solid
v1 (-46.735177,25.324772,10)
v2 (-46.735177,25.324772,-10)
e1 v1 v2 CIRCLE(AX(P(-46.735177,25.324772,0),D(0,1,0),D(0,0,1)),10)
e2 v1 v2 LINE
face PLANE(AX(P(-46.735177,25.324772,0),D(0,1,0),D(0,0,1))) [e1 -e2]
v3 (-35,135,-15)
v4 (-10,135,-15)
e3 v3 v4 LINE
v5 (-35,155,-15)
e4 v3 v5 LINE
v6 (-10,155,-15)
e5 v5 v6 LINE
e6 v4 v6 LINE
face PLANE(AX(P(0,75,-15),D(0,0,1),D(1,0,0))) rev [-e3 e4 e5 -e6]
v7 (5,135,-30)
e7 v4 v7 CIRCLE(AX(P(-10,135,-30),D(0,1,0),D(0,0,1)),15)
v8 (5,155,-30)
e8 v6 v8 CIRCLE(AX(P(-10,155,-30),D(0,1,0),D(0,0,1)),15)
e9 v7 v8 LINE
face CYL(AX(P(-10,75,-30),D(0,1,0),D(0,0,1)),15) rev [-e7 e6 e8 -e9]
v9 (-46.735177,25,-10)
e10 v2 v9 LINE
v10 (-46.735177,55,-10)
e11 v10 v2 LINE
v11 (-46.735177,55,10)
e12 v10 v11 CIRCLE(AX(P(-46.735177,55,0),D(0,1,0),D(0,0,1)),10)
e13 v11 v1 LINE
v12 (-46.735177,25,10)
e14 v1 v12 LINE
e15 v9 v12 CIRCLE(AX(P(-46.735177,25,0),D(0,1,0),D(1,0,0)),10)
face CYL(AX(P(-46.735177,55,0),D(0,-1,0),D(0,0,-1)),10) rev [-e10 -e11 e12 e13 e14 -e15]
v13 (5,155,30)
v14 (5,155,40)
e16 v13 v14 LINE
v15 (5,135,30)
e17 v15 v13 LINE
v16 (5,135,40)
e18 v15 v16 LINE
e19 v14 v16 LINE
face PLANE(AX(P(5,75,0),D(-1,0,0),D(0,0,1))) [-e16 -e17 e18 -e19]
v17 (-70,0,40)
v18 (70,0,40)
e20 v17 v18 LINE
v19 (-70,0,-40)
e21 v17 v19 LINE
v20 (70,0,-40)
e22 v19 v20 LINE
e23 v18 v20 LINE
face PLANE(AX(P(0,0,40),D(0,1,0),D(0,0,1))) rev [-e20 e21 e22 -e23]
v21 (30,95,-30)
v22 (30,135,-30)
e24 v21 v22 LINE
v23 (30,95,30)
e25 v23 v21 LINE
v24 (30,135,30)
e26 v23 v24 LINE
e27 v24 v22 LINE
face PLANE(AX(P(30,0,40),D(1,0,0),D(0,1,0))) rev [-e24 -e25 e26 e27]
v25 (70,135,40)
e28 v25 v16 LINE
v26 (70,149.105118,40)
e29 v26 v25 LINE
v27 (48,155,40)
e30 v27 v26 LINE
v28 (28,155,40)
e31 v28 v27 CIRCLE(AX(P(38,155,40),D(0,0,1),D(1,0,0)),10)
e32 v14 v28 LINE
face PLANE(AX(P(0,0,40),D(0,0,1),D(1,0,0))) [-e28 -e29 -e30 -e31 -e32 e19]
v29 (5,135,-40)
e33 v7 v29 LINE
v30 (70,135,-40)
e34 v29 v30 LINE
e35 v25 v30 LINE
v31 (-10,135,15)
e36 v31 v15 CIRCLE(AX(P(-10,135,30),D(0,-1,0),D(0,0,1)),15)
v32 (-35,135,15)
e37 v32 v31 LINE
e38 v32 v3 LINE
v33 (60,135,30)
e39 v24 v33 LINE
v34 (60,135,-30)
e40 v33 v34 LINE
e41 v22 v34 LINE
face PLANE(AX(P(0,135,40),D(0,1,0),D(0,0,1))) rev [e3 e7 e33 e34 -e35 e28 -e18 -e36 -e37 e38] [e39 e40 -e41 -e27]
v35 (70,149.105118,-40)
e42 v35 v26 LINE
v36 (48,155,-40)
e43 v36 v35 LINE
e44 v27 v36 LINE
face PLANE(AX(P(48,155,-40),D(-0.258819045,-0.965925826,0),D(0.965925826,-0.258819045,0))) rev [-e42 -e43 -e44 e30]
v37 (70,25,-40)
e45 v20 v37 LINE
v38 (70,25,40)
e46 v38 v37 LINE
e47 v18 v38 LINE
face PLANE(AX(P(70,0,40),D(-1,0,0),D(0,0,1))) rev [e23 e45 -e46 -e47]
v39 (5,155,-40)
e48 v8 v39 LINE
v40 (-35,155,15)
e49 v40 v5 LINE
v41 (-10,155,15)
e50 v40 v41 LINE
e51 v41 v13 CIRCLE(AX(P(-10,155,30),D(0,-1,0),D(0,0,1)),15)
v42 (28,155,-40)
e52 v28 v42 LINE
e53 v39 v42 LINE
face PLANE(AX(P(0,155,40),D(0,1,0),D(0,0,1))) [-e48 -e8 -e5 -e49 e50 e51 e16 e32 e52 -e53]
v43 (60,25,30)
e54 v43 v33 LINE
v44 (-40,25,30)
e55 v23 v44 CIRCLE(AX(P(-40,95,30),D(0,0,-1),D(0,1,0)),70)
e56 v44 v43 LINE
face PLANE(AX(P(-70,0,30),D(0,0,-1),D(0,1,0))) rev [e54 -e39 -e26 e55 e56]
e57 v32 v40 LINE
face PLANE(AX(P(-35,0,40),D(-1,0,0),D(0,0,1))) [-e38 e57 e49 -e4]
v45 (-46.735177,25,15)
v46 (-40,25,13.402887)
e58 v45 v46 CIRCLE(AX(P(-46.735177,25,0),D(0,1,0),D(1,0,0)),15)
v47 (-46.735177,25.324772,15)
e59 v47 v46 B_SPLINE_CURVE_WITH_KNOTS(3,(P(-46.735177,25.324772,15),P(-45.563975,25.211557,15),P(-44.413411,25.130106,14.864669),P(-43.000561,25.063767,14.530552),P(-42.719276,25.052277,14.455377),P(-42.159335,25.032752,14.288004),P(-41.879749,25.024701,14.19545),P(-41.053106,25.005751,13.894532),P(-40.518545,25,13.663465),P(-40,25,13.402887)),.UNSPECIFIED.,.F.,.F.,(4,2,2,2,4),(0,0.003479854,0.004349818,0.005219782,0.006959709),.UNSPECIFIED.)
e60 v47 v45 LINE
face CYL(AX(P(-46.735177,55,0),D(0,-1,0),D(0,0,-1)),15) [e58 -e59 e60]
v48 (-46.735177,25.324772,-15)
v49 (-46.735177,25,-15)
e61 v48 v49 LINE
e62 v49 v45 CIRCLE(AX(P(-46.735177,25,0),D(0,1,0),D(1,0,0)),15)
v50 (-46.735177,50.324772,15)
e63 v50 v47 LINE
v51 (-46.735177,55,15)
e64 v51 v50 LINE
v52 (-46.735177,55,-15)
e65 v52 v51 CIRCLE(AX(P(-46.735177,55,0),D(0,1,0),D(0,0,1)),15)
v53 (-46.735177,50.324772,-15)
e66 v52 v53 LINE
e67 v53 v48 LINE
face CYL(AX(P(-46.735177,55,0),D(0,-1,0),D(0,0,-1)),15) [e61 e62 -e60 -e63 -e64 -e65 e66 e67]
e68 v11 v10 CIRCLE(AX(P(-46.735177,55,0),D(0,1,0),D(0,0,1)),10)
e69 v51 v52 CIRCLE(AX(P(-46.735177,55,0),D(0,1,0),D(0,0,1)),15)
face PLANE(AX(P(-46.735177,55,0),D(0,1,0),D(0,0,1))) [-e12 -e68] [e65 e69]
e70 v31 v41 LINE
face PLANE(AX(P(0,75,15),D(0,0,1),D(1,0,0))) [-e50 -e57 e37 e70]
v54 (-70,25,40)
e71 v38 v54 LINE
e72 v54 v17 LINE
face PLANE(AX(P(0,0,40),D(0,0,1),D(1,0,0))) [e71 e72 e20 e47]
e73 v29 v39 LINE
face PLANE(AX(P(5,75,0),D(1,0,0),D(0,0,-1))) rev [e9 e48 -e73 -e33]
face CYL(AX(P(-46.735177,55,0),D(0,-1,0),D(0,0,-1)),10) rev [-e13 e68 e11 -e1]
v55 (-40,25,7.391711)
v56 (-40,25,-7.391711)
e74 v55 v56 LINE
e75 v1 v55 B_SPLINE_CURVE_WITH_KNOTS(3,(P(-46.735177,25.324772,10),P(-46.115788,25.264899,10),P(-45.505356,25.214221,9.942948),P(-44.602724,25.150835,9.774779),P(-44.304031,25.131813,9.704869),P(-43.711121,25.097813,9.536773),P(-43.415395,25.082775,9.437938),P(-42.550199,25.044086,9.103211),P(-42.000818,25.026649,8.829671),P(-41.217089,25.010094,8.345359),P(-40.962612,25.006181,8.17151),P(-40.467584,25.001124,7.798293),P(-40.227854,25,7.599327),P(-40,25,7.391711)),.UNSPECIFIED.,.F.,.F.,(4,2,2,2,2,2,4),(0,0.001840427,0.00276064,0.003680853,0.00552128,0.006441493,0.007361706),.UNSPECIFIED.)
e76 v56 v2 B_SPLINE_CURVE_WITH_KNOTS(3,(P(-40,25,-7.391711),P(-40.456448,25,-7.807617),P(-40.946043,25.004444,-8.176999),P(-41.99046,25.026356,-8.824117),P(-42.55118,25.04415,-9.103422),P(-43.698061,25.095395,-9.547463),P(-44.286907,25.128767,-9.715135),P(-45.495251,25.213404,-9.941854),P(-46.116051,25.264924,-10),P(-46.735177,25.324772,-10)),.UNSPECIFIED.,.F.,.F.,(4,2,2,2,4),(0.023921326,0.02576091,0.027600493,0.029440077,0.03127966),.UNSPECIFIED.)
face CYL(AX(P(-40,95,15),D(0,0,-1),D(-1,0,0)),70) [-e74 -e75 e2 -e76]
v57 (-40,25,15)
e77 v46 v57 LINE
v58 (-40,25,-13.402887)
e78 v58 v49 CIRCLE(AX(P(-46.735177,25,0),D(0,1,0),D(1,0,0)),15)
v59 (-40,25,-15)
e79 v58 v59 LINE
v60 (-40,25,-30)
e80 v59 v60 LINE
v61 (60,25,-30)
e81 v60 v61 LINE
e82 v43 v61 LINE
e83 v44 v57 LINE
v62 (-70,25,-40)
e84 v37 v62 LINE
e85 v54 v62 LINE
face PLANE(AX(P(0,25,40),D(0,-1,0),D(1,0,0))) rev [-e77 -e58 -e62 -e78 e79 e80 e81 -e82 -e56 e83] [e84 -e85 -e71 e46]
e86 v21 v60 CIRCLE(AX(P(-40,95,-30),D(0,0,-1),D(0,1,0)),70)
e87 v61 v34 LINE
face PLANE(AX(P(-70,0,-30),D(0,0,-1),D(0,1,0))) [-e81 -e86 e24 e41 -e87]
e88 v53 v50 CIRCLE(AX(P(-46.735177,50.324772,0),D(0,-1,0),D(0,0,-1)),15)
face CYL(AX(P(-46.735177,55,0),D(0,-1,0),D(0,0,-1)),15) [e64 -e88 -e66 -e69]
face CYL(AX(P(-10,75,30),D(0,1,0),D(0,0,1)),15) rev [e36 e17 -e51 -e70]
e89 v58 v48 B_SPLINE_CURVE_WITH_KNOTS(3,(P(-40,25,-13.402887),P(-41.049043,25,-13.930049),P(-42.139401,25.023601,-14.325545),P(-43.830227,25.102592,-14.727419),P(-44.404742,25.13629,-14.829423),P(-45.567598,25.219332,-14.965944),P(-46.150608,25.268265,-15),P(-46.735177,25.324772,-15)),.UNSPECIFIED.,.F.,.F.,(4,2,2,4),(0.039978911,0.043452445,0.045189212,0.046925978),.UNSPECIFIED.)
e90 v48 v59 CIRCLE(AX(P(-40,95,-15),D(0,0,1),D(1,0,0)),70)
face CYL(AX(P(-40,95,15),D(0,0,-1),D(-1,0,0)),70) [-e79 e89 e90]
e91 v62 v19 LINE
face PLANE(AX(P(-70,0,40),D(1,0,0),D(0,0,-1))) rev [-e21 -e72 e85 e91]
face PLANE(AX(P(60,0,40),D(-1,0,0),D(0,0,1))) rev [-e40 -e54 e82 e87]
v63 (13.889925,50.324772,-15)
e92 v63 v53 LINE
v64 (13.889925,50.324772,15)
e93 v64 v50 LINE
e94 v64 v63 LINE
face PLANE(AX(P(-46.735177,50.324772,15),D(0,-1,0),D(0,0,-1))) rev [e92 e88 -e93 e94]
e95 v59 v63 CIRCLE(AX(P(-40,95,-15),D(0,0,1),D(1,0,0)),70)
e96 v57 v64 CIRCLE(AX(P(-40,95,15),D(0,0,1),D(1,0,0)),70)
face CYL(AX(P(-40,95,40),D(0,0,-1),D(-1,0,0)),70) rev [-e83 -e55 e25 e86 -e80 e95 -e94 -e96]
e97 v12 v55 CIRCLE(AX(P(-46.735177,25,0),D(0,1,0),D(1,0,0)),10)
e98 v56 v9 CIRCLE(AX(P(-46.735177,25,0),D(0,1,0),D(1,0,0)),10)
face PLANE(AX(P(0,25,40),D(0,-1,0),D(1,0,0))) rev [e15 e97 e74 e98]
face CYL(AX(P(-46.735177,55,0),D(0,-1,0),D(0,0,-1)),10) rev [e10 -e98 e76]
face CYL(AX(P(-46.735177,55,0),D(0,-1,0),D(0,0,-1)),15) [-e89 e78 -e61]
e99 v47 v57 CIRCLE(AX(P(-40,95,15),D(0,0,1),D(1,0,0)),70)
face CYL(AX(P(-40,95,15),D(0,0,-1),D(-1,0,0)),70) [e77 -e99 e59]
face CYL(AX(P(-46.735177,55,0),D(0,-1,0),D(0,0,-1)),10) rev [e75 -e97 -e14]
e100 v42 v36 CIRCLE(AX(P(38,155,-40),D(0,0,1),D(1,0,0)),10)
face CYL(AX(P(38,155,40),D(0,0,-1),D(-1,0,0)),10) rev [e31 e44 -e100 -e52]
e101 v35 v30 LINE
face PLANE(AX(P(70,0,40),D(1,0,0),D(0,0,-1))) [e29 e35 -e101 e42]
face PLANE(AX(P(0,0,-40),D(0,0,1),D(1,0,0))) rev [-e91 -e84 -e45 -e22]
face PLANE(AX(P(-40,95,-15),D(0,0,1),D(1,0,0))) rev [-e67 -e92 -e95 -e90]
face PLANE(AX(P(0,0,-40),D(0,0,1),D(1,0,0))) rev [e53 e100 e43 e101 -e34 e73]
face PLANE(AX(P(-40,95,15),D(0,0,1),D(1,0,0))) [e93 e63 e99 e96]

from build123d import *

# Parameters (mm, degrees)
BRACKET_BODY_DEPTH          = 40
BASE_RECESS_SKETCH_W        = 10
BASE_RECESS_SKETCH_H        = 110
BASE_RECESS_CUT_DEPTH       = 207.215906273
CRADLE_GROOVE_R15_DEPTH     = 80
TOP_CHAMFER_CUT_15DEG_DEPTH = 80
PIN_BOSS_SKETCH_R           = 15
PIN_BOSS_SKETCH_R_2         = 10
PIN_BOSS_DEPTH              = 55
CURVED_WEB_DEPTH            = 15
PIN_START                   = -25
PIN_BORE_SKETCH_R           = 10
PIN_BORE_20_DEPTH           = 25


with BuildPart() as part:
    # Bracket Profile Sketch → Bracket Body (new, symmetric)
    with BuildSketch(Plane.XY):
        with BuildLine():
            Line((-40, 25), (60, 25))
            Line((60, 25), (60, 135))
            Line((60, 135), (70, 135))
            Line((70, 135), (70, 155))
            Line((70, 155), (48, 155))
            ThreePointArc((48, 155), (38, 145), (28, 155))
            Line((28, 155), (-35, 155))
            Line((-35, 155), (-35, 135))
            Line((-35, 135), (30, 135))
            Line((30, 135), (30, 95))
            ThreePointArc((30, 95), (9.497474683, 45.502525317), (-40, 25))
        make_face()
        Polygon((-70, 25), (-70, 0), (0, 0), (70, 0), (70, 25), align=None)
    extrude(amount=BRACKET_BODY_DEPTH, both=True)

    # Base Recess Sketch → Base Recess Cut (cut, through all)
    with BuildSketch(Plane(origin=(60, 0, 0), x_dir=(0, 0, -1), z_dir=(1, 0, 0))):
        with Locations((35, 80)):
            Rectangle(BASE_RECESS_SKETCH_W, BASE_RECESS_SKETCH_H)
        with Locations((-35, 80)):
            Rectangle(BASE_RECESS_SKETCH_W, BASE_RECESS_SKETCH_H)
    extrude(amount=-BASE_RECESS_CUT_DEPTH, mode=Mode.SUBTRACT)

    # Cradle Groove Sketch → Cradle Groove R15 (cut)
    with BuildSketch(Plane(origin=(0, 155, 0), x_dir=(1, 0, 0), z_dir=(0, 1, 0))):
        with BuildLine():
            Line((-35, 40), (-35, 15))
            Line((-35, 15), (-10, 15))
            ThreePointArc((-10, 15), (0.606601718, 19.393398282), (5, 30))
            Line((5, 30), (5, 40))
            Line((5, 40), (-35, 40))
        make_face()
        with BuildLine():
            Line((-10, -15), (-35, -15))
            Line((-35, -15), (-35, -40))
            Line((-35, -40), (5, -40))
            Line((5, -40), (5, -30))
            ThreePointArc((5, -30), (0.606601718, -19.393398282), (-10, -15))
        make_face()
    extrude(amount=-CRADLE_GROOVE_R15_DEPTH, mode=Mode.SUBTRACT)

    # Top Chamfer Sketch → Top Chamfer Cut 15deg (cut)
    with BuildSketch(Plane.XY.offset(40)):
        Polygon((48, 155), (70, 149.105117767), (70, 155), align=None)
    extrude(amount=-TOP_CHAMFER_CUT_15DEG_DEPTH, mode=Mode.SUBTRACT)

    # Pin Boss Sketch → Pin Boss (add)
    with BuildSketch(Plane(origin=(0, 0, 0), x_dir=(1, 0, 0), z_dir=(0, 1, 0))):
        with Locations(Location((-46.735177318, 0, 0), (0, 0, 63.319698917))):
            Circle(PIN_BOSS_SKETCH_R)
        with Locations(Location((-46.735177318, 0, 0), (0, 0, 47.660850918))):
            Circle(PIN_BOSS_SKETCH_R_2, mode=Mode.SUBTRACT)
    extrude(amount=PIN_BOSS_DEPTH)

    # Curved Web Sketch → Curved Web (add, symmetric)
    with BuildSketch(Plane.XY):
        with BuildLine():
            Line((-46.735177318, 25.324772074), (-46.735177318, 50.324772074))
            Line((-46.735177318, 50.324772074), (13.889924938, 50.324772074))
            ThreePointArc((13.889924938, 50.324772074), (-13.314000754, 30.286342676), (-46.735177318, 25.324772074))
        make_face()
    extrude(amount=CURVED_WEB_DEPTH, both=True)

    # Pin Bore Sketch → Pin Bore Ø20 (cut)
    with BuildSketch(Plane(origin=(0, 50.324772074, 0), x_dir=(1, 0, 0), z_dir=(0, 1, 0)).offset(PIN_START)):
        with Locations(Location((-46.735177318, 0, 0), (0, 0, 270))):
            Circle(PIN_BORE_SKETCH_R)
    extrude(amount=PIN_BORE_20_DEPTH, mode=Mode.SUBTRACT)


solid = part.part
